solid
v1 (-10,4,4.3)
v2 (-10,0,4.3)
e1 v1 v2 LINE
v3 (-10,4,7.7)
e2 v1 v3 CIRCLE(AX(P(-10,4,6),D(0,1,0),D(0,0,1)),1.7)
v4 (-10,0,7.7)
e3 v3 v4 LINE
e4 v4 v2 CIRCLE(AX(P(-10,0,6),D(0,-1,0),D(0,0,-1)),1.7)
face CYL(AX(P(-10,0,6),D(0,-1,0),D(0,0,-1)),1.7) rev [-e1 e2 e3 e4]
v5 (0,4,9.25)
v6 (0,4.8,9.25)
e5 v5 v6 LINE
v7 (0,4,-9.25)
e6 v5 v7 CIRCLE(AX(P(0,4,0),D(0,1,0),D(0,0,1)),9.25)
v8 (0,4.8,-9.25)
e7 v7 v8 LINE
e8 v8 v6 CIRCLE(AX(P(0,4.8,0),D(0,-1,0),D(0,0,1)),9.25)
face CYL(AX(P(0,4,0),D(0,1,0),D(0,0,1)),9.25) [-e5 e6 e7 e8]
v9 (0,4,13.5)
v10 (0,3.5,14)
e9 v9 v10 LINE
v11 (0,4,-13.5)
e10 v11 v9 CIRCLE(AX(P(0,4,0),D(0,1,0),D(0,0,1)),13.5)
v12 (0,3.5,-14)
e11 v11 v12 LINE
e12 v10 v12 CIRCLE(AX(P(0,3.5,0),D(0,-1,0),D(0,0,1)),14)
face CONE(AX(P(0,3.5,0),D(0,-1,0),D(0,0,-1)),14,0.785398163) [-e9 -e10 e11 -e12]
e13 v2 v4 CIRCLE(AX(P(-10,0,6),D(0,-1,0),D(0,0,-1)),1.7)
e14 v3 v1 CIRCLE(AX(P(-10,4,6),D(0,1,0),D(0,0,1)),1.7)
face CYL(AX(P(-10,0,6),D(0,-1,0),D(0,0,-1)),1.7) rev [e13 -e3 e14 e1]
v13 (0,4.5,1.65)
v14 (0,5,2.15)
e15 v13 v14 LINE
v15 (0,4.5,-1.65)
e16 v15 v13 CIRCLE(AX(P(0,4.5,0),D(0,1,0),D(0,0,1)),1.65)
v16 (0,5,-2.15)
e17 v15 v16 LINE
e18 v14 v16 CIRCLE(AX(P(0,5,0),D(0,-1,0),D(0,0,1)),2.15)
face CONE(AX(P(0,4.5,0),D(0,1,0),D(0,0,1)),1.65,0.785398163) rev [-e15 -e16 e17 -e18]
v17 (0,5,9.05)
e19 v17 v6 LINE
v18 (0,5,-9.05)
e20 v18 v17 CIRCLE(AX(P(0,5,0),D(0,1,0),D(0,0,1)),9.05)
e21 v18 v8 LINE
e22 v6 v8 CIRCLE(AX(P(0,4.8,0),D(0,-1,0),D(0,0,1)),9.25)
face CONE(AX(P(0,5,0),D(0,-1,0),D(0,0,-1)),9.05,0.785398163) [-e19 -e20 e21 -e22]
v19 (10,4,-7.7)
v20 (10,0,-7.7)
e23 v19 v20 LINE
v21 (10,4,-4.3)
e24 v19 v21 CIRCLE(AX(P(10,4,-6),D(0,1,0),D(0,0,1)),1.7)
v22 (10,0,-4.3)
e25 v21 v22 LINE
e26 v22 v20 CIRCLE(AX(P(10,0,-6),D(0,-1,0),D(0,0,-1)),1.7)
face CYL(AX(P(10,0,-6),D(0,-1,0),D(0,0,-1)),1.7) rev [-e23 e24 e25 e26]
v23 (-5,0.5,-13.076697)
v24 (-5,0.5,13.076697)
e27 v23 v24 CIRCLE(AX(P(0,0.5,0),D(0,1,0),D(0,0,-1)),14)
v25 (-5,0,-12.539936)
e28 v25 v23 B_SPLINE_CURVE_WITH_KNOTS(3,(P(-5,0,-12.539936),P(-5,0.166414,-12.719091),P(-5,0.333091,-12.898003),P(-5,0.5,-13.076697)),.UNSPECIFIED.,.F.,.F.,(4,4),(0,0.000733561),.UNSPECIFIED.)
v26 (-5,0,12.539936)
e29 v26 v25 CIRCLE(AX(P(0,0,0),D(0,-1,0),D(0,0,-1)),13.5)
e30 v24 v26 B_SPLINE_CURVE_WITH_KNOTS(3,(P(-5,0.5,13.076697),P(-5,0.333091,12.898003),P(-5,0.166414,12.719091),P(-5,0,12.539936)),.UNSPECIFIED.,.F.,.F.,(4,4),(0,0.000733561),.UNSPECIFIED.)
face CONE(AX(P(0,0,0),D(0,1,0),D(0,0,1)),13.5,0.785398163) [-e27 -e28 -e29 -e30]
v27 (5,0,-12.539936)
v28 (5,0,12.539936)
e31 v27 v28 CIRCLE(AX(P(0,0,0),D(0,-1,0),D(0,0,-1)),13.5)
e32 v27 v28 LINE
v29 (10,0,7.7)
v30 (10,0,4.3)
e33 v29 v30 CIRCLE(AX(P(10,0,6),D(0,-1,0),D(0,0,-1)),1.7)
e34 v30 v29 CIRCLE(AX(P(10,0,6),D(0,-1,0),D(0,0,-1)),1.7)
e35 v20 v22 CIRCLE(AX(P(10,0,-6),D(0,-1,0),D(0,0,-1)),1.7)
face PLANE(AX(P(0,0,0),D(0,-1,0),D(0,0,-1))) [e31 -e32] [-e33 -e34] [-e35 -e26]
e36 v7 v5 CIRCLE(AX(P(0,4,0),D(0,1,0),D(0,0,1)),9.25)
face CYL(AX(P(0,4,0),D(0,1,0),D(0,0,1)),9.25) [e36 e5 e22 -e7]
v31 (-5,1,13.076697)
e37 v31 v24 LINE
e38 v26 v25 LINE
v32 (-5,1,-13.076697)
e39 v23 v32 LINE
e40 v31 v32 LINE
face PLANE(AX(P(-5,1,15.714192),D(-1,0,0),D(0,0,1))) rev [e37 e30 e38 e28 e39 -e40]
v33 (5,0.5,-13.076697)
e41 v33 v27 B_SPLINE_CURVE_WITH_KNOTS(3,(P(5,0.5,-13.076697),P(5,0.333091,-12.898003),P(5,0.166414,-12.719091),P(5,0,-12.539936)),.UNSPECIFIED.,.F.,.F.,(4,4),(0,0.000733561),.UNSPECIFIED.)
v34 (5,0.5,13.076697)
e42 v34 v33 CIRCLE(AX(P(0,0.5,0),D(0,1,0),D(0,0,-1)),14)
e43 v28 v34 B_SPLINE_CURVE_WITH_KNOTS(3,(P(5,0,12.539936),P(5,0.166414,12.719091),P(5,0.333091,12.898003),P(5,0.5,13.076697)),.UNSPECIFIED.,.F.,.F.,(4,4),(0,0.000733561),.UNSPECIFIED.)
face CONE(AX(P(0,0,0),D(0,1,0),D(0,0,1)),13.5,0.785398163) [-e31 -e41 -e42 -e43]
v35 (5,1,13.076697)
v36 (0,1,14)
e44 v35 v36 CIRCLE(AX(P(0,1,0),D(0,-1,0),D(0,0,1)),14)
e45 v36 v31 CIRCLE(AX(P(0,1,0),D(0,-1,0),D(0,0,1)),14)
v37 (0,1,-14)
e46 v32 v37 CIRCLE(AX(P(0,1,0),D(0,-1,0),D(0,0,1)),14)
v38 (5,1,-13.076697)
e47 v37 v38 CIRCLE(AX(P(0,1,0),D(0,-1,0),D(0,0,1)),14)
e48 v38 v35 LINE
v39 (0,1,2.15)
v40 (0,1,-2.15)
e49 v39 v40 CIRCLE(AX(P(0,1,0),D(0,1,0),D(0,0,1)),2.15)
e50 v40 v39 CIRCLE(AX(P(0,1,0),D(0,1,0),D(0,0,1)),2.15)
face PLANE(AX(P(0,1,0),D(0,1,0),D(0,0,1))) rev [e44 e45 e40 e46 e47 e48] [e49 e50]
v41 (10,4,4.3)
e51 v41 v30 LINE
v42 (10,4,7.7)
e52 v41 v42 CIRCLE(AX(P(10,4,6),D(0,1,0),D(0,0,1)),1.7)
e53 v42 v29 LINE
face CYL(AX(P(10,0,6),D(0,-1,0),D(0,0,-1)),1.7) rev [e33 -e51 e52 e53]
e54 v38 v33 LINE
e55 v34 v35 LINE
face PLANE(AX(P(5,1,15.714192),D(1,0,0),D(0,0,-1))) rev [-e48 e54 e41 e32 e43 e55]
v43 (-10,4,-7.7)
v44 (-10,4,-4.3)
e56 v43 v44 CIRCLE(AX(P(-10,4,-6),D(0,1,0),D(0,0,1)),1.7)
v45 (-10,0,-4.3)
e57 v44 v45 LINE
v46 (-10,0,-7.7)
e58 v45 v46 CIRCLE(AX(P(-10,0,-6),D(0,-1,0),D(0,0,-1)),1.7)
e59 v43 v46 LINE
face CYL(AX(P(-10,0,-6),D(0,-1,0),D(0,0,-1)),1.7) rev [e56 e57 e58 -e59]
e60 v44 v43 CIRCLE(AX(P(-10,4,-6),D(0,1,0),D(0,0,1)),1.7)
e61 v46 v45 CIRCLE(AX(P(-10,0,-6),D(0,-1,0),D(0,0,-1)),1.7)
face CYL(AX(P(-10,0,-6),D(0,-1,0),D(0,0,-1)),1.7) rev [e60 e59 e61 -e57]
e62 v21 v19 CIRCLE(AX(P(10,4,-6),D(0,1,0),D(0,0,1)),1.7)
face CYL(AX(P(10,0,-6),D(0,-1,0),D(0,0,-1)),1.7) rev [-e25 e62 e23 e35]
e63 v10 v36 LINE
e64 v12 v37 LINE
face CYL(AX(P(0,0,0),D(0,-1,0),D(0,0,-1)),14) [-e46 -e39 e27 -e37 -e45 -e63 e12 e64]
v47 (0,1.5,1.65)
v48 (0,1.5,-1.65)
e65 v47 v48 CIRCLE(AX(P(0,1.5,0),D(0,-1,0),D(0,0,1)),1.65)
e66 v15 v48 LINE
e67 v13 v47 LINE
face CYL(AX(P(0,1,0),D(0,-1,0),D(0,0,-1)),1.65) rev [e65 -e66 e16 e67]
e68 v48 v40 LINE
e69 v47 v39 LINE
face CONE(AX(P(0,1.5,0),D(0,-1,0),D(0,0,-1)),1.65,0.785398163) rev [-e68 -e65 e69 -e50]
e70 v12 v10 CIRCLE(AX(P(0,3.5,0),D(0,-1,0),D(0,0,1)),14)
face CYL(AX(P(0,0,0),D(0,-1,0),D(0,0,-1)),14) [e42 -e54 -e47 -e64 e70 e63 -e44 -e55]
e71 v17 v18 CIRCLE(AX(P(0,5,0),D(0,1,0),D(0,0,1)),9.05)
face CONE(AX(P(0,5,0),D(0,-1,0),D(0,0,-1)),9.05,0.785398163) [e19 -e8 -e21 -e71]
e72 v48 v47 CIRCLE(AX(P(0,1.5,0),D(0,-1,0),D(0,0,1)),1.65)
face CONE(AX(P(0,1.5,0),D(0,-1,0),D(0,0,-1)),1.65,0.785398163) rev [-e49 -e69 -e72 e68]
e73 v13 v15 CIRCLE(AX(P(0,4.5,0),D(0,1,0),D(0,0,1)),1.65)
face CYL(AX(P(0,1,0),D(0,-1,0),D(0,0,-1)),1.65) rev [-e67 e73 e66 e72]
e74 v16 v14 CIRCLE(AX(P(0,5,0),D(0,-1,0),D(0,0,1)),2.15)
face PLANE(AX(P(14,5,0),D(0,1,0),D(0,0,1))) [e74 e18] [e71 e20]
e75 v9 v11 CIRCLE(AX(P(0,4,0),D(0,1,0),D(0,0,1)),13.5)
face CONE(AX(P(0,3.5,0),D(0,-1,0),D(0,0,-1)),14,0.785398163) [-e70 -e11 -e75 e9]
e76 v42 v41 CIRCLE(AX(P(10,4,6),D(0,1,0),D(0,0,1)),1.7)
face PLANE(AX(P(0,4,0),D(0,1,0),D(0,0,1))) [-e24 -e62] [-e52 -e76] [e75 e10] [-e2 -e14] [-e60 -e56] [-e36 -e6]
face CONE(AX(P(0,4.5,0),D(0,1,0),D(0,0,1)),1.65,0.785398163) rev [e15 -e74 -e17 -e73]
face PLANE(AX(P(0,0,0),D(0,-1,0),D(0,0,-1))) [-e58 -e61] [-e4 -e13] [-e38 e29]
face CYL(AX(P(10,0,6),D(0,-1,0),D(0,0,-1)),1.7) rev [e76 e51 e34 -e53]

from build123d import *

# Parameters (mm, degrees)
SKETCH1_W            = 14
SKETCH1_H            = 5
SKETCH3_OUTSIDE_W    = 37.982
SKETCH3_OUTSIDE_H    = 37.982
SKETCH3_OUTSIDE_R    = 9.25
CUT_EXTRUDE2_DEPTH   = 1
M3_CLEARANCE_HOLE1_D = 3.4
SKETCH6_W            = 10
SKETCH6_H            = 31.428384658
CUT_EXTRUDE3_DEPTH   = 1
M4_TAPPED_HOLE1_D    = 3.3
CHAMFER1_SIZE        = 0.5
CHAMFER2_SIZE        = 0.2


with BuildPart() as part:
    # Sketch1 → Revolve1 (revolve)
    with BuildSketch(Plane.XY, mode=Mode.PRIVATE) as revolve1_sk:
        with Locations((7, 2.5)):
            Rectangle(SKETCH1_W, SKETCH1_H)
    revolve(revolve1_sk.sketch.rotate(Axis((0, 0, 0), (0, 1, 0)), 90), axis=Axis((0, 0, 0), (0, 1, 0)))

    # Sketch3 outside → Cut-Extrude2 (cut)
    with BuildSketch(Plane(origin=(0, 5, 0), x_dir=(1, 0, 0), z_dir=(0, 1, 0))):
        Rectangle(SKETCH3_OUTSIDE_W, SKETCH3_OUTSIDE_H)
        with Locations(Location((0, 0, 0), (0, 0, 270))):
            Circle(SKETCH3_OUTSIDE_R, mode=Mode.SUBTRACT)
    extrude(amount=-CUT_EXTRUDE2_DEPTH, mode=Mode.SUBTRACT)

    # M3 Clearance Hole1 (through all)
    with Locations(Plane(origin=(0, 0, 0), x_dir=(-1, 0, 0), z_dir=(0, -1, 0))):
        with Locations((10, -6), (10, 6), (-10, -6), (-10, 6)):
            Hole(M3_CLEARANCE_HOLE1_D / 2)

    # Sketch6 → Cut-Extrude3 (cut)
    with BuildSketch(Plane.XZ):
        Rectangle(SKETCH6_W, SKETCH6_H)
    extrude(amount=-CUT_EXTRUDE3_DEPTH, mode=Mode.SUBTRACT)

    # M4 Tapped Hole1 (through all)
    with Locations(Plane(origin=(0, 1, 0), x_dir=(-1, 0, 0), z_dir=(0, -1, 0))):
        with Locations((0, 0)):
            Hole(M4_TAPPED_HOLE1_D / 2)

    # Chamfer1
    chamfer1_edges = [part.edges().sort_by_distance(p)[0] for p in [
        (0, 4, 14),
        (14, 0, 0),
        (-14, 0, 0),
        (-1.65, 1, 0),
        (-1.65, 5, 0),
    ]]
    chamfer(chamfer1_edges, length=CHAMFER1_SIZE)

    # Chamfer2
    chamfer2_edges = [part.edges().sort_by_distance(p)[0] for p in [
        (0, 5, -9.25),
    ]]
    chamfer(chamfer2_edges, length=CHAMFER2_SIZE)


solid = part.part
